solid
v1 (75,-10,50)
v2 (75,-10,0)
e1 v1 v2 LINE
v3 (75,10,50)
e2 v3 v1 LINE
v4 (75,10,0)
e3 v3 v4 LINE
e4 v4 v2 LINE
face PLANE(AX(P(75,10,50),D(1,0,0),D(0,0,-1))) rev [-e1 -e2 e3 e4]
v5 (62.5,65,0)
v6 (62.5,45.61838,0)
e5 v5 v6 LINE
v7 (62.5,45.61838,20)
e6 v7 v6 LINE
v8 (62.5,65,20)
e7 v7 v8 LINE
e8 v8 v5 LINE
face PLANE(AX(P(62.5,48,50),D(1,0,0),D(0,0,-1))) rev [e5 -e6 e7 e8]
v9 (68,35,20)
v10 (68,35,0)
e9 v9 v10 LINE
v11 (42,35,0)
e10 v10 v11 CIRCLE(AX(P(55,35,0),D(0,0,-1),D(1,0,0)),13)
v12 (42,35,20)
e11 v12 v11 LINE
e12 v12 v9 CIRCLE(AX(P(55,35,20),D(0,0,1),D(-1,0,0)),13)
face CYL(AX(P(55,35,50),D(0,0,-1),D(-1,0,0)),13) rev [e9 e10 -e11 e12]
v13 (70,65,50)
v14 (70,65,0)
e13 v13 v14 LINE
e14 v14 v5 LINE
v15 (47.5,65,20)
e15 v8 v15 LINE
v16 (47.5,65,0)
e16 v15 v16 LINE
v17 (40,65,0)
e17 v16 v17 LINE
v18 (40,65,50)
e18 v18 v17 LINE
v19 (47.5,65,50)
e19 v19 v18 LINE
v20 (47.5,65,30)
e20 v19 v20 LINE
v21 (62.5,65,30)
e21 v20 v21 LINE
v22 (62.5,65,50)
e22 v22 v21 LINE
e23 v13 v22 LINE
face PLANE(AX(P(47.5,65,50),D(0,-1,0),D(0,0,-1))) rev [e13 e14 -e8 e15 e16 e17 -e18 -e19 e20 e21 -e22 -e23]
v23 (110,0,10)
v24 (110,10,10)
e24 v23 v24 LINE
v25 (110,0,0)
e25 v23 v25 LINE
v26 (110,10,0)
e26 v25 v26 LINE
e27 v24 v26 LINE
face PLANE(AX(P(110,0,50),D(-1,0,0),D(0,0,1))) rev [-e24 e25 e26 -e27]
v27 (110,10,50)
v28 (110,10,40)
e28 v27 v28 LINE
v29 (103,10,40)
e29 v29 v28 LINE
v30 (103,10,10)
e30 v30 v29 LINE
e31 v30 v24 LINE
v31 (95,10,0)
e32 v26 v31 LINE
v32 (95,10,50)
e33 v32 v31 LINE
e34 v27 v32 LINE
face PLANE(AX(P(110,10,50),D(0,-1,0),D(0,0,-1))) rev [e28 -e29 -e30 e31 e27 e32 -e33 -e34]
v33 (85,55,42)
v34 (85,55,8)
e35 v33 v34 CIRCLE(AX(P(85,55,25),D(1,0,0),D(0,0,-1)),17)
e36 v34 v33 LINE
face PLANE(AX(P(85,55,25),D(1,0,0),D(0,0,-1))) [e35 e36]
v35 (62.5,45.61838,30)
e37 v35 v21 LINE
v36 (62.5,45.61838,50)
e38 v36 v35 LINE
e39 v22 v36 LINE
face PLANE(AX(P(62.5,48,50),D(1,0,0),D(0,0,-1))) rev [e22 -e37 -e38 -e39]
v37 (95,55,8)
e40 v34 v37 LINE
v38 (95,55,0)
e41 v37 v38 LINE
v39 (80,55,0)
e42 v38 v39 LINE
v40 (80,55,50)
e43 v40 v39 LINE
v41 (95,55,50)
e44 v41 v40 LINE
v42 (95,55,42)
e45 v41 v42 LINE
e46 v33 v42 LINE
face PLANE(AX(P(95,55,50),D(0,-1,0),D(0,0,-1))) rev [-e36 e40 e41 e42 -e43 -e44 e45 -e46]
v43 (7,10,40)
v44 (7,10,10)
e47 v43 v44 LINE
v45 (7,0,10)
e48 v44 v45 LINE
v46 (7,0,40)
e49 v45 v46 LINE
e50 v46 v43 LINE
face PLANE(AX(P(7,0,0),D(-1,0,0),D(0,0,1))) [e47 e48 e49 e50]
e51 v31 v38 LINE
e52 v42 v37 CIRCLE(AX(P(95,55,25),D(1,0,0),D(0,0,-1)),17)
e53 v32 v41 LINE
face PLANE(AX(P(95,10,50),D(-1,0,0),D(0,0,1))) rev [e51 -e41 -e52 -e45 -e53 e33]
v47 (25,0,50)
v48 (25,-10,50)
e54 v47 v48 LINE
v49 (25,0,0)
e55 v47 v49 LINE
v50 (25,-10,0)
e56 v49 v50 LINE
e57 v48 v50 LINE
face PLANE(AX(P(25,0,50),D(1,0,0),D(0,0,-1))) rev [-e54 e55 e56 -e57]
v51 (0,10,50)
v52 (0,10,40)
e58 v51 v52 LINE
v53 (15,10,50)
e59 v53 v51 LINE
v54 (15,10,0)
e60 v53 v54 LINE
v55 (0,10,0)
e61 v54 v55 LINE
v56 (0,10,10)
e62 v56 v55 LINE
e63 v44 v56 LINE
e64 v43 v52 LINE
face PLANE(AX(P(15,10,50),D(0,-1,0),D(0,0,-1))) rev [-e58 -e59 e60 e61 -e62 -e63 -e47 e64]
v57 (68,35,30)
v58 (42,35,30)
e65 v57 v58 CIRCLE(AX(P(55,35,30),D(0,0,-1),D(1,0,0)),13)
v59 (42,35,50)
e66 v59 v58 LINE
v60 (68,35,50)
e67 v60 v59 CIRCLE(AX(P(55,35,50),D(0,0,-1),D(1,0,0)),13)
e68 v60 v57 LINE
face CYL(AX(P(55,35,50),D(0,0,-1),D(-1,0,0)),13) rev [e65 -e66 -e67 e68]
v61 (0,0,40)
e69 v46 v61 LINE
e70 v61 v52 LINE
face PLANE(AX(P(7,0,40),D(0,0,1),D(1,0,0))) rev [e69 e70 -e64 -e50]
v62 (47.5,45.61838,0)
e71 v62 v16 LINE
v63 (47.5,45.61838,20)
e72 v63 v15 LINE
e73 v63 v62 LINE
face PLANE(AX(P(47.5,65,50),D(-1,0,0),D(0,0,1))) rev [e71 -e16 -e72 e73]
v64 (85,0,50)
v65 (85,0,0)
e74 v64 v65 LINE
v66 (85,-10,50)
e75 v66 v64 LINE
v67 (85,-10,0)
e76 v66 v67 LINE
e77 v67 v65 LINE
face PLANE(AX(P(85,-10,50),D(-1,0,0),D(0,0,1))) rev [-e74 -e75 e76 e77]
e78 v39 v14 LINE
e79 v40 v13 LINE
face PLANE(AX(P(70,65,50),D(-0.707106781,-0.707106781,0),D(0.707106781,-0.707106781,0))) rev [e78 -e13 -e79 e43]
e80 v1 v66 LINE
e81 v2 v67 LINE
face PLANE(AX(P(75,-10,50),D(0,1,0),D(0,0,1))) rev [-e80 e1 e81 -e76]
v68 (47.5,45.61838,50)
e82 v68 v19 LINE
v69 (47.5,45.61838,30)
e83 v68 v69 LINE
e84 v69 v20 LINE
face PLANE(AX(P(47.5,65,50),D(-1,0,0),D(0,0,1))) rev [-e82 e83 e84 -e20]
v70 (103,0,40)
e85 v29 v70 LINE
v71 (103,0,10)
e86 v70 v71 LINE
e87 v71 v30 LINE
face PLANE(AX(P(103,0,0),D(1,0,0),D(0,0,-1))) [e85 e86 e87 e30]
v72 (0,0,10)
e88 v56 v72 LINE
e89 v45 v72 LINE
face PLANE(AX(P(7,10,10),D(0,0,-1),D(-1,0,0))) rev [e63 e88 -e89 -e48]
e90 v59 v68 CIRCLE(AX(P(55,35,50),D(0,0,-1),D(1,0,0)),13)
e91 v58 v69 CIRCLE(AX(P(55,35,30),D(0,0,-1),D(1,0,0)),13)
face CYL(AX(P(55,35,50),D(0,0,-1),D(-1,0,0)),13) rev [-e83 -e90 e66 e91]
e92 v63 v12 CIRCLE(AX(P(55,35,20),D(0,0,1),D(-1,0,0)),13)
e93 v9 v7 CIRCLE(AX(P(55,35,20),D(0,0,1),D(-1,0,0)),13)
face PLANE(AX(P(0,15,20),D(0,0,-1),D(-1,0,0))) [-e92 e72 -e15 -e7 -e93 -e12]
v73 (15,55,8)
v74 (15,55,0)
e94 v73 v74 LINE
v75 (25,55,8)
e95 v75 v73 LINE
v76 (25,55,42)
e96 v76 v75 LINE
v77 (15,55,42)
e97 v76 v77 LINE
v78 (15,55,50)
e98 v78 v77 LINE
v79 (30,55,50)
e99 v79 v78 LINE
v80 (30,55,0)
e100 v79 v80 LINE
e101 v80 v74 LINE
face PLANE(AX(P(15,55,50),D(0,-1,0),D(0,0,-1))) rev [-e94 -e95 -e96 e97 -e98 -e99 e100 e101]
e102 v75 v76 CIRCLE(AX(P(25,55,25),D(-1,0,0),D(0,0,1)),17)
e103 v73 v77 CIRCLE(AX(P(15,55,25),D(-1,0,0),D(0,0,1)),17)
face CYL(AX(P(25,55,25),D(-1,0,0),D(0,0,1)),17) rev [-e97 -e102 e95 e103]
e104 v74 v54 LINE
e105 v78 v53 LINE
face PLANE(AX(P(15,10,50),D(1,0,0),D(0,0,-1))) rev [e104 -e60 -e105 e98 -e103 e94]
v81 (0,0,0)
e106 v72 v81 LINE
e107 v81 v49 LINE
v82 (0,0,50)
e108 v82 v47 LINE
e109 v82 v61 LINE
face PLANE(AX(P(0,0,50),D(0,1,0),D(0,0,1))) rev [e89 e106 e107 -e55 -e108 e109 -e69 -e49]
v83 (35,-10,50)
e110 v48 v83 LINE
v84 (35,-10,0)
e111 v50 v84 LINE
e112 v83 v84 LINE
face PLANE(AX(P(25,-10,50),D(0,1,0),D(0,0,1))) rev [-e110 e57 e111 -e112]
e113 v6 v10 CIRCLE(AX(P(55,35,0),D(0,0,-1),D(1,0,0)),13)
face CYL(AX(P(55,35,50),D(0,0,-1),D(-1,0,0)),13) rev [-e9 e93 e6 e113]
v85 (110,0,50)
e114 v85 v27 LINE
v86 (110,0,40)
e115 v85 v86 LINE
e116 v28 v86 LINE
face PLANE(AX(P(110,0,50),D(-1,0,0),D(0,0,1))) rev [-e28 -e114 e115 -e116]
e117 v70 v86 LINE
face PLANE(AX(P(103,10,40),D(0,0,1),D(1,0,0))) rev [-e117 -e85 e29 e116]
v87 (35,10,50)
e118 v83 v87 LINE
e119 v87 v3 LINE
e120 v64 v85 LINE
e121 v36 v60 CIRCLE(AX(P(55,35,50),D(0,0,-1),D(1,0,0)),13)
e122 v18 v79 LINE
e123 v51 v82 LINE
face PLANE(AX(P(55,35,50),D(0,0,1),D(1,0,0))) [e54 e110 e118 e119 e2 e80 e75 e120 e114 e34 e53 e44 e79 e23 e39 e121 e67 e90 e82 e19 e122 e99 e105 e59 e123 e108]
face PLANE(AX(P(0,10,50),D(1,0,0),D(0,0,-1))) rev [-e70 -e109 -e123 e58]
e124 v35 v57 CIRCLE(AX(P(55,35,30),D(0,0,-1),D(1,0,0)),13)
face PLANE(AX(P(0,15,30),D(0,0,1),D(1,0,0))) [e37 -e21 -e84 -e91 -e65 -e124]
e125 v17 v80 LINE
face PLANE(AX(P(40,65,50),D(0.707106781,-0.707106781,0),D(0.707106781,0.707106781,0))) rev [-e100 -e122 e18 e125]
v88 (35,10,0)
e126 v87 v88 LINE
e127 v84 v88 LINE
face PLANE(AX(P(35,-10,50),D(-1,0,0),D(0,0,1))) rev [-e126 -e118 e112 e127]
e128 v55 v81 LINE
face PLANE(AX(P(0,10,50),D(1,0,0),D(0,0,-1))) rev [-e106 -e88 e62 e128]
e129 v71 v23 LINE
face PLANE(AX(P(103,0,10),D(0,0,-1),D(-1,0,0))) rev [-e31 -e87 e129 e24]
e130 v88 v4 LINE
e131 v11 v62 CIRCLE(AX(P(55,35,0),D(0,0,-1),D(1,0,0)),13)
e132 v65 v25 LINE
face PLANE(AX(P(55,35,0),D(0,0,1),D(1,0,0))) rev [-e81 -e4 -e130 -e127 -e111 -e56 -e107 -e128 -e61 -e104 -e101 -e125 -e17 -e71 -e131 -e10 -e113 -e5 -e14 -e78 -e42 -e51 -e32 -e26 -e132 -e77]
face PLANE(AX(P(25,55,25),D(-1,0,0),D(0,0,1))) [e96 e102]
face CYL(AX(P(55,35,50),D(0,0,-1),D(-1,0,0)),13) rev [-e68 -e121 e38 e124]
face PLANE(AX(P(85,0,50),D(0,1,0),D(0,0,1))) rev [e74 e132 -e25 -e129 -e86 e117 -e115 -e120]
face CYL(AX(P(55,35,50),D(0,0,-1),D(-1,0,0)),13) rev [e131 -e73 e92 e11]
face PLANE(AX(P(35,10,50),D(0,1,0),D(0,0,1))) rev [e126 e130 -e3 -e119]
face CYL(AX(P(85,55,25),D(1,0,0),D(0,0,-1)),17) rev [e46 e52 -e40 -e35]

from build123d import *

# Parameters (mm, degrees)
BASE_BODY_DEPTH          = 50
UPPER_BLOCK_DEPTH        = 50
CENTRE_START             = -10
CENTRE_WEB_DEPTH         = 10
FOOT_SLOT_1_DEPTH        = 7
FOOT_SLOT_2_DEPTH        = 7
BEARING_SEAT_CUT_1_DEPTH = 10
BEARING_START            = -10
BEARING_SEAT_CUT_2_DEPTH = 10


with BuildPart() as part:
    # Base Body Profile Sketch → Base Body (new body)
    with BuildSketch(Plane.XY):
        with BuildLine():
            Line((0, 0), (25, 0))
            Line((25, 0), (25, -10))
            Line((25, -10), (35, -10))
            Line((35, -10), (35, 10))
            Line((35, 10), (75, 10))
            Line((75, 10), (75, -10))
            Line((75, -10), (85, -10))
            Line((85, -10), (85, 0))
            Line((85, 0), (110, 0))
            Line((110, 0), (110, 10))
            Line((110, 10), (95, 10))
            Line((95, 10), (95, 55))
            Line((95, 55), (80, 55))
            Line((80, 55), (70, 65))
            Line((70, 65), (62.5, 65))
            Line((62.5, 65), (62.5, 48))
            Line((62.5, 48), (62.5, 45.618380291))
            ThreePointArc((62.5, 45.618380291), (55, 22), (47.5, 45.618380291))
            Line((47.5, 45.618380291), (47.5, 48))
            Line((47.5, 48), (47.5, 65))
            Line((47.5, 65), (40, 65))
            Line((40, 65), (30, 55))
            Line((30, 55), (15, 55))
            Line((15, 55), (15, 10))
            Line((15, 10), (0, 10))
            Line((0, 10), (0, 0))
        make_face()
    extrude(amount=BASE_BODY_DEPTH)

    # Upper Block Sketch → Upper Block (add)
    with BuildSketch(Plane(origin=(0, 65, 0), x_dir=(1, 0, 0), z_dir=(0, 1, 0))):
        Polygon((47.5, -20), (47.5, -25), (47.5, -30), (62.5, -30), (62.5, -20), align=None)
    extrude(amount=-UPPER_BLOCK_DEPTH)

    # Centre Web Sketch → Centre Web (add)
    with BuildSketch(Plane.XY.offset(30).offset(CENTRE_START)):
        with BuildLine():
            Line((47.5, 45.618380291), (47.5, 24.381619709))
            ThreePointArc((47.5, 24.381619709), (42, 35), (47.5, 45.618380291))
        make_face()
        with BuildLine():
            Line((62.5, 45.618380291), (62.5, 24.381619709))
            ThreePointArc((62.5, 24.381619709), (68, 35), (62.5, 45.618380291))
        make_face()
    extrude(amount=CENTRE_WEB_DEPTH)

    # Foot Slot 1 Sketch → Foot Slot 1 (cut)
    with BuildSketch(Plane.ZY):
        Polygon((25, 10), (10, 10), (10, 0), (40, 0), (40, 10), align=None)
    extrude(amount=-FOOT_SLOT_1_DEPTH, mode=Mode.SUBTRACT)

    # Foot Slot 2 Sketch → Foot Slot 2 (cut)
    with BuildSketch(Plane(origin=(110, 0, 0), x_dir=(0, 0, -1), z_dir=(1, 0, 0))):
        Polygon((-25, 10), (-40, 10), (-40, 0), (-10, 0), (-10, 10), align=None)
    extrude(amount=-FOOT_SLOT_2_DEPTH, mode=Mode.SUBTRACT)

    # Bearing Seat Cut 1 Sketch → Bearing Seat Cut 1 (cut)
    with BuildSketch(Plane(origin=(95, 0, 0), x_dir=(0, 0, -1), z_dir=(1, 0, 0))):
        with BuildLine():
            Line((-42, 55), (-8, 55))
            ThreePointArc((-8, 55), (-25, 38), (-42, 55))
        make_face()
    extrude(amount=-BEARING_SEAT_CUT_1_DEPTH, mode=Mode.SUBTRACT)

    # Bearing Seat Cut 2 Sketch → Bearing Seat Cut 2 (cut)
    with BuildSketch(Plane.ZY.offset(-15).offset(BEARING_START)):
        with BuildLine():
            Line((8, 55), (42, 55))
            ThreePointArc((42, 55), (25, 38), (8, 55))
        make_face()
    extrude(amount=BEARING_SEAT_CUT_2_DEPTH, mode=Mode.SUBTRACT)


solid = part.part
